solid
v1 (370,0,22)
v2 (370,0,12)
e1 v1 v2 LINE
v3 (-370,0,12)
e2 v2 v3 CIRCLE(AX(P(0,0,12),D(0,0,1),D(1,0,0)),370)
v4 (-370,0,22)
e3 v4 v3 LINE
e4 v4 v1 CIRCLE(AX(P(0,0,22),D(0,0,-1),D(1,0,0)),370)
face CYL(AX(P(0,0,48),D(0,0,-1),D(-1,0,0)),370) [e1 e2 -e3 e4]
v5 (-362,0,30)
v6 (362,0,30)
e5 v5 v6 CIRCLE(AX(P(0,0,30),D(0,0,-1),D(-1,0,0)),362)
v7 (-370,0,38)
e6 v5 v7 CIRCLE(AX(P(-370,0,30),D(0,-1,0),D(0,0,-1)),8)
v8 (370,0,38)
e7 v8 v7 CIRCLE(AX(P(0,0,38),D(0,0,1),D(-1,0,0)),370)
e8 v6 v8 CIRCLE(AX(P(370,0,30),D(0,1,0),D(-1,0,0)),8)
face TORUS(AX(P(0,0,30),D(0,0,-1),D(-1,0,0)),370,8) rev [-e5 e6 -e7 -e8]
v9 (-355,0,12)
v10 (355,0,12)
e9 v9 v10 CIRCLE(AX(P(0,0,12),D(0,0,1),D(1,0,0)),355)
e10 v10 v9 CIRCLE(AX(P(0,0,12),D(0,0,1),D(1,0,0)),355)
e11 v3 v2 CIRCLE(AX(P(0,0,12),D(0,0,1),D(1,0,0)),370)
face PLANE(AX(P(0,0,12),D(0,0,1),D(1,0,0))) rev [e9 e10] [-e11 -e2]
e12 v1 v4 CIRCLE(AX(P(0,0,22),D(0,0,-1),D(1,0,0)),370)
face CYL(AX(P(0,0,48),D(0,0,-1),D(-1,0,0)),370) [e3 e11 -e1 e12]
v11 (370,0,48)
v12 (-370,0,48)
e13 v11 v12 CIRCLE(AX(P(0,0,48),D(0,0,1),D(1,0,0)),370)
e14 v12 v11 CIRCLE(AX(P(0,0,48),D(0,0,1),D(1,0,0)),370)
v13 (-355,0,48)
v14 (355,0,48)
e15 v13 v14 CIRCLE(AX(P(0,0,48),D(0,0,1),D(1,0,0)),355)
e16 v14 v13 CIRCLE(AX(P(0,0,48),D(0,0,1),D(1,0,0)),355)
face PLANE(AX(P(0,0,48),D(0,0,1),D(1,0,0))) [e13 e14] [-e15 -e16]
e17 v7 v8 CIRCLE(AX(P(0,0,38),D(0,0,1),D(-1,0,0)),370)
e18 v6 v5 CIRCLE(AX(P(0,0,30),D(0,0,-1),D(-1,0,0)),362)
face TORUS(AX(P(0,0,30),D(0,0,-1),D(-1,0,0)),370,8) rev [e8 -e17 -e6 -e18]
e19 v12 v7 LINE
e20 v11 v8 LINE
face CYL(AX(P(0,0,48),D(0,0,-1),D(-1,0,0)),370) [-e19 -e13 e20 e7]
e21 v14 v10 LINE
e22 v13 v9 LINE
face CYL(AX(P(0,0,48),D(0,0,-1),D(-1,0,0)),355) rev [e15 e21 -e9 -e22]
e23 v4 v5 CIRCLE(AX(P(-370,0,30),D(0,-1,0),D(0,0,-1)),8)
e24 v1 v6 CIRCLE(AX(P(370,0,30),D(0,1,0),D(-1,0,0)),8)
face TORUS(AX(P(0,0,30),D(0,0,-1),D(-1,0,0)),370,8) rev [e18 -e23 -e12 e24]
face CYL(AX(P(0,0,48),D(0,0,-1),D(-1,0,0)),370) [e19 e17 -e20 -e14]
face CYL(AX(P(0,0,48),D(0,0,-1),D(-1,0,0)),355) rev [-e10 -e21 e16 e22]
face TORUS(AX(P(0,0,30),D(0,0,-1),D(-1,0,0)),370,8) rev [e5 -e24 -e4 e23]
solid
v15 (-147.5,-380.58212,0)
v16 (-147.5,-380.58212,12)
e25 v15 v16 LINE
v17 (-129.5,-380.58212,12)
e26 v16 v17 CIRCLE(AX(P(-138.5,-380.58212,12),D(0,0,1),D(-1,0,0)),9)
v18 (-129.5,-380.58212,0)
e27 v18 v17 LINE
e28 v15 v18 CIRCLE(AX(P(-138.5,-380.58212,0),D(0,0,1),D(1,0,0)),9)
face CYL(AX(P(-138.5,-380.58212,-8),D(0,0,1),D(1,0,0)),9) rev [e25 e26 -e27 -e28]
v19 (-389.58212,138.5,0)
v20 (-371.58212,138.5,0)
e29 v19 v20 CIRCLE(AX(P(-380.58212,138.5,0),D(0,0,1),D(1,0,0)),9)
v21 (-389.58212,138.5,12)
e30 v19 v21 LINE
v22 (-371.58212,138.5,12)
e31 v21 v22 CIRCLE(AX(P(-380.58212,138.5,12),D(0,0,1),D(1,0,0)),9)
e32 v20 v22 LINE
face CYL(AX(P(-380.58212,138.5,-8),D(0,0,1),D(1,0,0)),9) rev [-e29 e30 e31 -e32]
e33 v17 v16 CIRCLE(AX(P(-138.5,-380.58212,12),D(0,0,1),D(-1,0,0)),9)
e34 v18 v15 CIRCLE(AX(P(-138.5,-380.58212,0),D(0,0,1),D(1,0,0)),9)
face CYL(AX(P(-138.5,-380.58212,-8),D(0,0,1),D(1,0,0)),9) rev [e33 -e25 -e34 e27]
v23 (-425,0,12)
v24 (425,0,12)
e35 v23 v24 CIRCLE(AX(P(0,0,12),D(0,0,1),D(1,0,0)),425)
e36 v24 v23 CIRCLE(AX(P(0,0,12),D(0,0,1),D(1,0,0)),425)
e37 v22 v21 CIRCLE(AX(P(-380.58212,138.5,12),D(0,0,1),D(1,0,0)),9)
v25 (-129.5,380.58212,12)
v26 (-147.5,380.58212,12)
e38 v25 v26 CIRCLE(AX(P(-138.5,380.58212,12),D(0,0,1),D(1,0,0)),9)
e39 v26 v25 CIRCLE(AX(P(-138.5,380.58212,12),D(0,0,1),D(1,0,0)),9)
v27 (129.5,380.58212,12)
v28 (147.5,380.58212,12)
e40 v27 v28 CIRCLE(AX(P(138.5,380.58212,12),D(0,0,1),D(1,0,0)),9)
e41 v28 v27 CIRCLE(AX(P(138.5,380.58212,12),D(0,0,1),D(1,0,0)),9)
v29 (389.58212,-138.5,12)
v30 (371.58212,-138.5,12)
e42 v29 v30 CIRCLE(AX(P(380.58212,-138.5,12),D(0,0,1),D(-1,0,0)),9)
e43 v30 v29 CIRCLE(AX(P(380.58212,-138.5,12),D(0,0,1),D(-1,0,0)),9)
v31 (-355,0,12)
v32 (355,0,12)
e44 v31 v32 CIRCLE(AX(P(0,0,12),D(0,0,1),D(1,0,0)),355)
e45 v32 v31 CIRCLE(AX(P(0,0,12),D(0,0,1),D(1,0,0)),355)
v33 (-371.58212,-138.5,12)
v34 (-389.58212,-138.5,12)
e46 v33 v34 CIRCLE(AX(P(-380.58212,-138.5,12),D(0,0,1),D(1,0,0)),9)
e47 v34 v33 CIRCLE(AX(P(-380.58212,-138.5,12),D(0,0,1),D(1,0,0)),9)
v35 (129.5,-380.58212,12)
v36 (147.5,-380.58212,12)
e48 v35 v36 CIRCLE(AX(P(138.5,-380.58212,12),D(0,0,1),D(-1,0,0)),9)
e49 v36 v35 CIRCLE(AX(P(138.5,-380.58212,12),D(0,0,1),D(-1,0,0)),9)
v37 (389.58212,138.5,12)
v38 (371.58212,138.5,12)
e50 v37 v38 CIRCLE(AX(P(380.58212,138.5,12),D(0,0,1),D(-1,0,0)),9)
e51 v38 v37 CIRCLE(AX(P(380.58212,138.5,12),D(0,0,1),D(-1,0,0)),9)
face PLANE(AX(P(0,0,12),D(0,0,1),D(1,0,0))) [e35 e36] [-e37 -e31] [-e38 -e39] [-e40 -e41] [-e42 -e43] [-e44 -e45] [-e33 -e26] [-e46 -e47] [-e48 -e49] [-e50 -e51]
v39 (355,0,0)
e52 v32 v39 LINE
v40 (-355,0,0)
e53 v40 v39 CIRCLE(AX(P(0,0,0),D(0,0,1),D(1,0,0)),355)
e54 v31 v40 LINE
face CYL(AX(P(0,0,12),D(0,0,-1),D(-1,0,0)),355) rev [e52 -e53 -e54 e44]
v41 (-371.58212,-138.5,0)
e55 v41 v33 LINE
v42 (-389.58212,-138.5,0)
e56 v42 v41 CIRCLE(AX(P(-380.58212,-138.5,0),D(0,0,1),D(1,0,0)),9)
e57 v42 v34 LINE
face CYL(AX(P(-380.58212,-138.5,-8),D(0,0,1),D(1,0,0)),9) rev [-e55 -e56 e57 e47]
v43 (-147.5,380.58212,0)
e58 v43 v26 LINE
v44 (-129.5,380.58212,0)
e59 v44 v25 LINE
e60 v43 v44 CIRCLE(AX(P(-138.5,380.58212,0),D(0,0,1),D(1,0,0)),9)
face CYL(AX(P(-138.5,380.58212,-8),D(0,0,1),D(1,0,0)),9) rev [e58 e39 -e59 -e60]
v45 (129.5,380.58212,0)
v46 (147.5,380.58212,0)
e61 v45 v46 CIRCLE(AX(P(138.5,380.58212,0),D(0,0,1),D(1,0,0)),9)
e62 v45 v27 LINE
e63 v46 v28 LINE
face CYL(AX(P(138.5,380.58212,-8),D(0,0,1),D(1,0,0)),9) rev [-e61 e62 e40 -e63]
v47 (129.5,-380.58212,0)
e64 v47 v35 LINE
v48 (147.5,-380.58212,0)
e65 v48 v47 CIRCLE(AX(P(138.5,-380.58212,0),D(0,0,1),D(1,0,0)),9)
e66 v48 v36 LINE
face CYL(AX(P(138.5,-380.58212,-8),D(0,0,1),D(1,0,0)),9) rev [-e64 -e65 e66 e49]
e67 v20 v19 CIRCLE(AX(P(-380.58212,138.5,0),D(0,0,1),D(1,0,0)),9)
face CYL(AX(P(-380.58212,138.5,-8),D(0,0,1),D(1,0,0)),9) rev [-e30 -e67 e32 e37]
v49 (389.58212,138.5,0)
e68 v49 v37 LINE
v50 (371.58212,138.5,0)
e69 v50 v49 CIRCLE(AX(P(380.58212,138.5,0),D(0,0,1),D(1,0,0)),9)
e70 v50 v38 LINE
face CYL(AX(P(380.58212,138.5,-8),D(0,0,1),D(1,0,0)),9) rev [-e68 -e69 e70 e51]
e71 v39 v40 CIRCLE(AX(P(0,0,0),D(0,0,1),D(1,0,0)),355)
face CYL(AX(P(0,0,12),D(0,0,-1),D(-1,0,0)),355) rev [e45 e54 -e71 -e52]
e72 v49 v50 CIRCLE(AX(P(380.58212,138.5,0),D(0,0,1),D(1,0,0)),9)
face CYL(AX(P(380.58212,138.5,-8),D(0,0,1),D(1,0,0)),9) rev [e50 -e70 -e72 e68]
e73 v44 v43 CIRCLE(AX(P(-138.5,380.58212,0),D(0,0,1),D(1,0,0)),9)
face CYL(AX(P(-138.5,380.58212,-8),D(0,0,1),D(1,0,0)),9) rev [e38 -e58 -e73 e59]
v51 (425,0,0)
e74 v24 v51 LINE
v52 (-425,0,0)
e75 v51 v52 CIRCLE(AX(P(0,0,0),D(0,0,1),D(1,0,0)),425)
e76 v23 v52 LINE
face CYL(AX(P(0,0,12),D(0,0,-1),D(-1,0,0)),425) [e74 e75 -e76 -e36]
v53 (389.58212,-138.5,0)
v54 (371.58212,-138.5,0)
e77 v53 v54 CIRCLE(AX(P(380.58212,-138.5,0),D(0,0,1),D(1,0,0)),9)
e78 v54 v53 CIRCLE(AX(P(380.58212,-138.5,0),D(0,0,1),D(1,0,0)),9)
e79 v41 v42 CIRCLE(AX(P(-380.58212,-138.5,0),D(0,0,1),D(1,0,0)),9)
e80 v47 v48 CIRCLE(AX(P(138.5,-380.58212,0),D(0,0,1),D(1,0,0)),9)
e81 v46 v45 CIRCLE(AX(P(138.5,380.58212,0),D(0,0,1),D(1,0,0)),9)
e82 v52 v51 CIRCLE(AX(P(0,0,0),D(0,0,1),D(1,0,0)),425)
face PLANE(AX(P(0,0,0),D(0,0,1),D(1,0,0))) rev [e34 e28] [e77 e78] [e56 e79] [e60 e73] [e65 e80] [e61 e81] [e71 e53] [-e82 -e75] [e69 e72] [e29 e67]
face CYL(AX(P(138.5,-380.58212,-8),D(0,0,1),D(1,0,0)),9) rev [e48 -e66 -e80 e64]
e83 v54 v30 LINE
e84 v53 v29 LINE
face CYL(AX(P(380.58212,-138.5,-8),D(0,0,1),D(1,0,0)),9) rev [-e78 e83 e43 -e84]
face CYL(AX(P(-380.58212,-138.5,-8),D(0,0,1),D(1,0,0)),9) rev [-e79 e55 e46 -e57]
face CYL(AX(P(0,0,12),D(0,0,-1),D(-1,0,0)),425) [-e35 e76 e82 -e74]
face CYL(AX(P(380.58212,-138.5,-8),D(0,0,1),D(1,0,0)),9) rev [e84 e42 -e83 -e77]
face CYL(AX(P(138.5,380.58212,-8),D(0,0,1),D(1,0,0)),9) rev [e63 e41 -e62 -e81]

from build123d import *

# Parameters (mm, degrees)
SKETCH_1_R          = 425
SKETCH_1_R_2        = 355
EXTRUDE_1_DEPTH     = 12
SKETCH_2_R          = 370
SKETCH_2_R_2        = 355
EXTRUDE_2_DEPTH     = 36
SWEEP_1_PROFILE_R   = 8
SKETCH_12_R         = 9
CUT_EXTRUDE_1_DEPTH = 20


with BuildPart() as part:
    # 草图1 → 凸台-拉伸1 (new body)
    with BuildSketch(Plane.XY):
        Circle(SKETCH_1_R)
        Circle(SKETCH_1_R_2, mode=Mode.SUBTRACT)
    extrude(amount=EXTRUDE_1_DEPTH)

    # 草图12 → 切除-拉伸1 (cut)
    with BuildSketch(Plane.XY.offset(12)):
        with Locations((-138.5, 380.582119916)):
            Circle(SKETCH_12_R)
        with Locations((138.5, 380.582119916)):
            Circle(SKETCH_12_R)
        with Locations((138.5, -380.582119916)):
            Circle(SKETCH_12_R)
        with Locations((-138.5, -380.582119916)):
            Circle(SKETCH_12_R)
        with Locations((-380.582119916, 138.5)):
            Circle(SKETCH_12_R)
        with Locations((-380.582119916, -138.5)):
            Circle(SKETCH_12_R)
        with Locations((380.582119916, -138.5)):
            Circle(SKETCH_12_R)
        with Locations((380.582119916, 138.5)):
            Circle(SKETCH_12_R)
    extrude(amount=-CUT_EXTRUDE_1_DEPTH, mode=Mode.SUBTRACT)


with BuildPart() as body_2:
    # 草图2 → 凸台-拉伸2 (new body)
    with BuildSketch(Plane.XY.offset(12)):
        Circle(SKETCH_2_R)
        Circle(SKETCH_2_R_2, mode=Mode.SUBTRACT)
    extrude(amount=EXTRUDE_2_DEPTH)

    # 切除-扫描1: sweep along a path in 草图3
    with BuildLine(Plane(origin=(0, 0, 30), x_dir=(-1, 0, 0), z_dir=(0, 0, -1))) as sweep_1_path:
        CenterArc((0, 0), 370, 0, 360)
    # 切除-扫描1 profile (on start of the path) → 切除-扫描1 (sweep, cut)
    with BuildSketch(Plane(origin=(-370, 0, 30), x_dir=(0, 0, 1), z_dir=(0, 1, 0))):
        Circle(SWEEP_1_PROFILE_R)
    sweep(path=sweep_1_path.line, mode=Mode.SUBTRACT)


solid = Compound([part.part, body_2.part])
